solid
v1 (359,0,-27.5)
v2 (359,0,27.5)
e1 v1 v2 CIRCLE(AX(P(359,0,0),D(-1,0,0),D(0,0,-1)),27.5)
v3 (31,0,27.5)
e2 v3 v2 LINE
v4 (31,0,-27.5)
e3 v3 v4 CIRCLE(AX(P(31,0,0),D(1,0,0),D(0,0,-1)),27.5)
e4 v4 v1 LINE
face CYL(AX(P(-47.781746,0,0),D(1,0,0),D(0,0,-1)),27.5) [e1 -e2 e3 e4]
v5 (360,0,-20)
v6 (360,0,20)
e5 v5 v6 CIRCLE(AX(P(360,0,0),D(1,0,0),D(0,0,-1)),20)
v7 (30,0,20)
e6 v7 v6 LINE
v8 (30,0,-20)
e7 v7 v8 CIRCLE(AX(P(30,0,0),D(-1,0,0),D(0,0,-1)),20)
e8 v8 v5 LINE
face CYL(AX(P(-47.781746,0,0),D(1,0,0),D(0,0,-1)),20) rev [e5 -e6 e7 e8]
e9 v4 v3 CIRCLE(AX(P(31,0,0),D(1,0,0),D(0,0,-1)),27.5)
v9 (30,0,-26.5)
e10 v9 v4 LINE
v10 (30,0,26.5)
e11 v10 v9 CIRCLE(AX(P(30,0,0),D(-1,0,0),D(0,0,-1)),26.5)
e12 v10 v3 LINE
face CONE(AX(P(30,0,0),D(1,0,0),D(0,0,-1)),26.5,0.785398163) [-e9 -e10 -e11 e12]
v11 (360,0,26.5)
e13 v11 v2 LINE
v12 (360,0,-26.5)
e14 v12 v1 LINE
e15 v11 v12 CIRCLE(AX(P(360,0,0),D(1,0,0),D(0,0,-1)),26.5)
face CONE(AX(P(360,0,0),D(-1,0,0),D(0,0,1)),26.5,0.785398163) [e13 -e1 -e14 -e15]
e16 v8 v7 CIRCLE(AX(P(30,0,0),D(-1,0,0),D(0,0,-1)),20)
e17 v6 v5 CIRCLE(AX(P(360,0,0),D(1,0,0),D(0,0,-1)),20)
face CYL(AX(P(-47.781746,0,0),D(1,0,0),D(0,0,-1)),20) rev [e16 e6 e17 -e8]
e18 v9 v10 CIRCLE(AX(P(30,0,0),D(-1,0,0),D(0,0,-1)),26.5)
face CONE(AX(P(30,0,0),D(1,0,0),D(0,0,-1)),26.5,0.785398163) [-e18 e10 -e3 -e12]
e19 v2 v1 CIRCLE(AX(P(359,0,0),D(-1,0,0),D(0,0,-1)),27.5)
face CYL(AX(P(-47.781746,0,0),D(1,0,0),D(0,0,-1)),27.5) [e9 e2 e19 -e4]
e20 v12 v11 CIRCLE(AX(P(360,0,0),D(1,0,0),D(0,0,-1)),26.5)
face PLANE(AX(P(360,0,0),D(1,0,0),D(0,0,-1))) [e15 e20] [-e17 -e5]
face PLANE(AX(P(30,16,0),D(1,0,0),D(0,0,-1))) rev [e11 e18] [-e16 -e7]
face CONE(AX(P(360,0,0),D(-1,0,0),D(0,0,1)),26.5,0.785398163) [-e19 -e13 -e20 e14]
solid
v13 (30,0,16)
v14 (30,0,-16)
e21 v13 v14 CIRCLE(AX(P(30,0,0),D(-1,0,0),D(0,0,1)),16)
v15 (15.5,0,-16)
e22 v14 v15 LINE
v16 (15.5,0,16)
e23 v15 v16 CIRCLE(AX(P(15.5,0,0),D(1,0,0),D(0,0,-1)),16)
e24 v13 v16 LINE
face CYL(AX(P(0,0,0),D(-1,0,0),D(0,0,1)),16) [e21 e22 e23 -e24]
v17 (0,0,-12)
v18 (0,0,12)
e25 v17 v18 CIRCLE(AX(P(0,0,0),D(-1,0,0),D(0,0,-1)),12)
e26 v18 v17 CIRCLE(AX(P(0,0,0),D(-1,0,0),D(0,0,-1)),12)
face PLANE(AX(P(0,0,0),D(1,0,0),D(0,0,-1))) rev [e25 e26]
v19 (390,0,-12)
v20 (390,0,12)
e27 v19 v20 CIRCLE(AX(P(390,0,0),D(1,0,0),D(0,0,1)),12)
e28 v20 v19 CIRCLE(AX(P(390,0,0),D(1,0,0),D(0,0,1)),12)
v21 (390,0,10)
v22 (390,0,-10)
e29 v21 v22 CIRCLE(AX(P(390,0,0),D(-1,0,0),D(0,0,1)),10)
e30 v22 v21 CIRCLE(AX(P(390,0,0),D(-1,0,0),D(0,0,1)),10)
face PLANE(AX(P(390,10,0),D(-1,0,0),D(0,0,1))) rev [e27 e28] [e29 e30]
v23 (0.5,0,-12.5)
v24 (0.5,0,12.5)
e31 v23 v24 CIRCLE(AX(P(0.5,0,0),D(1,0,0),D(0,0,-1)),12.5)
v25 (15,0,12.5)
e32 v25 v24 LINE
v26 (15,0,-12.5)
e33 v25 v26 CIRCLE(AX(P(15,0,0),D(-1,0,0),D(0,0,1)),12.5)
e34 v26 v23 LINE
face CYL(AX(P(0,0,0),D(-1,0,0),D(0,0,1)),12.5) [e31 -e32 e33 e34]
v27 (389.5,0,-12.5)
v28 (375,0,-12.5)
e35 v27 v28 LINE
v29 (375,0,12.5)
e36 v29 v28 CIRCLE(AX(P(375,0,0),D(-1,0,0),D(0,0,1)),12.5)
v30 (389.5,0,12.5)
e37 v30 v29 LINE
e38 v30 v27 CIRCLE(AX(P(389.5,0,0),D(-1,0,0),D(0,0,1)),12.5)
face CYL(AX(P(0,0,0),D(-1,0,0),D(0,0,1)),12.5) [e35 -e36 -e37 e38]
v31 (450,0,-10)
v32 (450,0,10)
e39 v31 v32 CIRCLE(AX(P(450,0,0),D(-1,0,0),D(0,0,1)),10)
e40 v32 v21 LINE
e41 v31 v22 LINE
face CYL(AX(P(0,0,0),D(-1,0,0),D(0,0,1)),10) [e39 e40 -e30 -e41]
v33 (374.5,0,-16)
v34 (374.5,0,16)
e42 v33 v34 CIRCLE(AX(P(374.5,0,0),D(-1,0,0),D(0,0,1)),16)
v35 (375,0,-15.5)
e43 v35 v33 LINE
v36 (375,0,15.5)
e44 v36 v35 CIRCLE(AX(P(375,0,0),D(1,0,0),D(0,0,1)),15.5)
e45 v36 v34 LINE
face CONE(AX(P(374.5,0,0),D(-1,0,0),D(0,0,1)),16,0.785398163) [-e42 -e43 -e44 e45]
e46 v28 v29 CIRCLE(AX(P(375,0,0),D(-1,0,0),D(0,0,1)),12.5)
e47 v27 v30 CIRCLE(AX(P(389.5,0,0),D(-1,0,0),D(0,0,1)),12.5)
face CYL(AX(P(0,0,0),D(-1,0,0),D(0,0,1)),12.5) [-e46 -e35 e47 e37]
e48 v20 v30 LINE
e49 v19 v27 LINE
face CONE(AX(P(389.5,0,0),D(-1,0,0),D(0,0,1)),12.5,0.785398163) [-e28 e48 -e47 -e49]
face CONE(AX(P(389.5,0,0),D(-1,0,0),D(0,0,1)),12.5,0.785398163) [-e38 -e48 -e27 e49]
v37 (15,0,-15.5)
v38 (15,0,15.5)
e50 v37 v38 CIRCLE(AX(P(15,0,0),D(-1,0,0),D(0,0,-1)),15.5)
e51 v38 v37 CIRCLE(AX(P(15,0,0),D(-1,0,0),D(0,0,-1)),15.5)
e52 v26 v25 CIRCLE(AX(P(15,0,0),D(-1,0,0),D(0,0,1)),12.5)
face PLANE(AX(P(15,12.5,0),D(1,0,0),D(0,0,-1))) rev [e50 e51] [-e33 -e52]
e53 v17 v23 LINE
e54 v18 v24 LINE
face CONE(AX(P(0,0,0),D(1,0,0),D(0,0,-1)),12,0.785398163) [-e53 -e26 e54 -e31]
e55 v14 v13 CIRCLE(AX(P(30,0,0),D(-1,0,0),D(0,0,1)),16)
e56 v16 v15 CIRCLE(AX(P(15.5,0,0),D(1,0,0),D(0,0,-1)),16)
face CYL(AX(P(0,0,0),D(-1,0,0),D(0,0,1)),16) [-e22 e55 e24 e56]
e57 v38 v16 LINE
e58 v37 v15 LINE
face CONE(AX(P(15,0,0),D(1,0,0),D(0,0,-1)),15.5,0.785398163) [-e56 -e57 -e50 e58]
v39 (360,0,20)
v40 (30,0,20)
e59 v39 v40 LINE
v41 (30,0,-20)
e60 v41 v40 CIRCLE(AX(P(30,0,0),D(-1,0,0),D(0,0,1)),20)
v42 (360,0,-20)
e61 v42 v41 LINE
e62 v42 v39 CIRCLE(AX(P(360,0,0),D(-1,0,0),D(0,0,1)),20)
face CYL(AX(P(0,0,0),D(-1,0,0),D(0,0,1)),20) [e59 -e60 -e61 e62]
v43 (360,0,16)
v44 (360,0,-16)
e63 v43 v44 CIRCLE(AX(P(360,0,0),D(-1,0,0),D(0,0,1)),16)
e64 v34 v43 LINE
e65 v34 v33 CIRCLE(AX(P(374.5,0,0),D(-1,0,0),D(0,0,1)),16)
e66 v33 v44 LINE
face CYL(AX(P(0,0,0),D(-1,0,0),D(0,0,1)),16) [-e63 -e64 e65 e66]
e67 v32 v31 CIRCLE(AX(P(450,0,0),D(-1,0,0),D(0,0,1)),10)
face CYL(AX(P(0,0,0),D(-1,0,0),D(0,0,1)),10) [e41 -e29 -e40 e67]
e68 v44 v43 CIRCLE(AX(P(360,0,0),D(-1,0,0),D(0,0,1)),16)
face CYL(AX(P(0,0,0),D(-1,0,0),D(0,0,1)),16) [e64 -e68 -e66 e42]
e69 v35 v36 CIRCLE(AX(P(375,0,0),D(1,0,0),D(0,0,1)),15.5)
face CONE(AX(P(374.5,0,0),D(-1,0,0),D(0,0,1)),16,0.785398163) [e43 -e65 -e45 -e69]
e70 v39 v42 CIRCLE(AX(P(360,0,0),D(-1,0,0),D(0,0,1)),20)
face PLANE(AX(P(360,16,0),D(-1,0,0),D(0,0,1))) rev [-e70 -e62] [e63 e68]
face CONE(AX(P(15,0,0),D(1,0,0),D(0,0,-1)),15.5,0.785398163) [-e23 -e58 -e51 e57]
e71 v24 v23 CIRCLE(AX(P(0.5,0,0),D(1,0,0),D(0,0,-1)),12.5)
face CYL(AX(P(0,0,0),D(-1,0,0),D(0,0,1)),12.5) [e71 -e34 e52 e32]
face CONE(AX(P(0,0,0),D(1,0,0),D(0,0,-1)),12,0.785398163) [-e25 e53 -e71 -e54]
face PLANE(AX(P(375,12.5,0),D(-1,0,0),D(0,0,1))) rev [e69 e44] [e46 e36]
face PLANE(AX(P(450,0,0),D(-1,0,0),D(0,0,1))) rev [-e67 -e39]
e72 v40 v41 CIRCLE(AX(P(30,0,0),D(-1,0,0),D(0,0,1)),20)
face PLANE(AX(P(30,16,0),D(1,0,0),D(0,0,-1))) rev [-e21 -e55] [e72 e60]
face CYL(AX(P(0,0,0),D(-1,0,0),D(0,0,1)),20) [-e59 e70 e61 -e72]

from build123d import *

# Parameters (mm, degrees)
SKETCH2_R           = 27.5
SKETCH2_R_2         = 20
BOSS_EXTRUDE1_DEPTH = 330
CHAMFER1_SIZE       = 0.5
CHAMFER2_SIZE       = 1


with BuildPart() as part:
    # Sketch1 → Revolve1 (revolve)
    with BuildSketch(Plane.XY, mode=Mode.PRIVATE) as revolve1_sk:
        Polygon((450, 10), (390, 10), (390, 12.5), (375, 12.5), (375, 16), (360, 16), (360, 20), (30, 20), (30, 16), (15, 16), (15, 12.5), (0, 12.5), (0, 0), (450, 0), align=None)
    revolve(revolve1_sk.sketch.rotate(Axis((0, 0, 0), (1, 0, 0)), 90), axis=Axis((0, 0, 0), (1, 0, 0)))

    # Chamfer1
    chamfer1_edges = [part.edges().sort_by_distance(p)[0] for p in [
        (15, 0, -16),
        (375, 0, -16),
        (390, 0, -12.5),
        (0, 0, -12.5),
    ]]
    chamfer(chamfer1_edges, length=CHAMFER1_SIZE)


with BuildPart() as body_2:
    # Sketch2 → Boss-Extrude1 (new body)
    with BuildSketch(Plane(origin=(360, 0, 0), x_dir=(0, 0, -1), z_dir=(1, 0, 0))):
        Circle(SKETCH2_R)
        Circle(SKETCH2_R_2, mode=Mode.SUBTRACT)
    extrude(amount=-BOSS_EXTRUDE1_DEPTH)

    # Chamfer2
    chamfer2_edges = [body_2.edges().sort_by_distance(p)[0] for p in [
        (360, 0, 27.5),
        (30, 0, 27.5),
    ]]
    chamfer(chamfer2_edges, length=CHAMFER2_SIZE)


solid = Compound([part.part, body_2.part])
